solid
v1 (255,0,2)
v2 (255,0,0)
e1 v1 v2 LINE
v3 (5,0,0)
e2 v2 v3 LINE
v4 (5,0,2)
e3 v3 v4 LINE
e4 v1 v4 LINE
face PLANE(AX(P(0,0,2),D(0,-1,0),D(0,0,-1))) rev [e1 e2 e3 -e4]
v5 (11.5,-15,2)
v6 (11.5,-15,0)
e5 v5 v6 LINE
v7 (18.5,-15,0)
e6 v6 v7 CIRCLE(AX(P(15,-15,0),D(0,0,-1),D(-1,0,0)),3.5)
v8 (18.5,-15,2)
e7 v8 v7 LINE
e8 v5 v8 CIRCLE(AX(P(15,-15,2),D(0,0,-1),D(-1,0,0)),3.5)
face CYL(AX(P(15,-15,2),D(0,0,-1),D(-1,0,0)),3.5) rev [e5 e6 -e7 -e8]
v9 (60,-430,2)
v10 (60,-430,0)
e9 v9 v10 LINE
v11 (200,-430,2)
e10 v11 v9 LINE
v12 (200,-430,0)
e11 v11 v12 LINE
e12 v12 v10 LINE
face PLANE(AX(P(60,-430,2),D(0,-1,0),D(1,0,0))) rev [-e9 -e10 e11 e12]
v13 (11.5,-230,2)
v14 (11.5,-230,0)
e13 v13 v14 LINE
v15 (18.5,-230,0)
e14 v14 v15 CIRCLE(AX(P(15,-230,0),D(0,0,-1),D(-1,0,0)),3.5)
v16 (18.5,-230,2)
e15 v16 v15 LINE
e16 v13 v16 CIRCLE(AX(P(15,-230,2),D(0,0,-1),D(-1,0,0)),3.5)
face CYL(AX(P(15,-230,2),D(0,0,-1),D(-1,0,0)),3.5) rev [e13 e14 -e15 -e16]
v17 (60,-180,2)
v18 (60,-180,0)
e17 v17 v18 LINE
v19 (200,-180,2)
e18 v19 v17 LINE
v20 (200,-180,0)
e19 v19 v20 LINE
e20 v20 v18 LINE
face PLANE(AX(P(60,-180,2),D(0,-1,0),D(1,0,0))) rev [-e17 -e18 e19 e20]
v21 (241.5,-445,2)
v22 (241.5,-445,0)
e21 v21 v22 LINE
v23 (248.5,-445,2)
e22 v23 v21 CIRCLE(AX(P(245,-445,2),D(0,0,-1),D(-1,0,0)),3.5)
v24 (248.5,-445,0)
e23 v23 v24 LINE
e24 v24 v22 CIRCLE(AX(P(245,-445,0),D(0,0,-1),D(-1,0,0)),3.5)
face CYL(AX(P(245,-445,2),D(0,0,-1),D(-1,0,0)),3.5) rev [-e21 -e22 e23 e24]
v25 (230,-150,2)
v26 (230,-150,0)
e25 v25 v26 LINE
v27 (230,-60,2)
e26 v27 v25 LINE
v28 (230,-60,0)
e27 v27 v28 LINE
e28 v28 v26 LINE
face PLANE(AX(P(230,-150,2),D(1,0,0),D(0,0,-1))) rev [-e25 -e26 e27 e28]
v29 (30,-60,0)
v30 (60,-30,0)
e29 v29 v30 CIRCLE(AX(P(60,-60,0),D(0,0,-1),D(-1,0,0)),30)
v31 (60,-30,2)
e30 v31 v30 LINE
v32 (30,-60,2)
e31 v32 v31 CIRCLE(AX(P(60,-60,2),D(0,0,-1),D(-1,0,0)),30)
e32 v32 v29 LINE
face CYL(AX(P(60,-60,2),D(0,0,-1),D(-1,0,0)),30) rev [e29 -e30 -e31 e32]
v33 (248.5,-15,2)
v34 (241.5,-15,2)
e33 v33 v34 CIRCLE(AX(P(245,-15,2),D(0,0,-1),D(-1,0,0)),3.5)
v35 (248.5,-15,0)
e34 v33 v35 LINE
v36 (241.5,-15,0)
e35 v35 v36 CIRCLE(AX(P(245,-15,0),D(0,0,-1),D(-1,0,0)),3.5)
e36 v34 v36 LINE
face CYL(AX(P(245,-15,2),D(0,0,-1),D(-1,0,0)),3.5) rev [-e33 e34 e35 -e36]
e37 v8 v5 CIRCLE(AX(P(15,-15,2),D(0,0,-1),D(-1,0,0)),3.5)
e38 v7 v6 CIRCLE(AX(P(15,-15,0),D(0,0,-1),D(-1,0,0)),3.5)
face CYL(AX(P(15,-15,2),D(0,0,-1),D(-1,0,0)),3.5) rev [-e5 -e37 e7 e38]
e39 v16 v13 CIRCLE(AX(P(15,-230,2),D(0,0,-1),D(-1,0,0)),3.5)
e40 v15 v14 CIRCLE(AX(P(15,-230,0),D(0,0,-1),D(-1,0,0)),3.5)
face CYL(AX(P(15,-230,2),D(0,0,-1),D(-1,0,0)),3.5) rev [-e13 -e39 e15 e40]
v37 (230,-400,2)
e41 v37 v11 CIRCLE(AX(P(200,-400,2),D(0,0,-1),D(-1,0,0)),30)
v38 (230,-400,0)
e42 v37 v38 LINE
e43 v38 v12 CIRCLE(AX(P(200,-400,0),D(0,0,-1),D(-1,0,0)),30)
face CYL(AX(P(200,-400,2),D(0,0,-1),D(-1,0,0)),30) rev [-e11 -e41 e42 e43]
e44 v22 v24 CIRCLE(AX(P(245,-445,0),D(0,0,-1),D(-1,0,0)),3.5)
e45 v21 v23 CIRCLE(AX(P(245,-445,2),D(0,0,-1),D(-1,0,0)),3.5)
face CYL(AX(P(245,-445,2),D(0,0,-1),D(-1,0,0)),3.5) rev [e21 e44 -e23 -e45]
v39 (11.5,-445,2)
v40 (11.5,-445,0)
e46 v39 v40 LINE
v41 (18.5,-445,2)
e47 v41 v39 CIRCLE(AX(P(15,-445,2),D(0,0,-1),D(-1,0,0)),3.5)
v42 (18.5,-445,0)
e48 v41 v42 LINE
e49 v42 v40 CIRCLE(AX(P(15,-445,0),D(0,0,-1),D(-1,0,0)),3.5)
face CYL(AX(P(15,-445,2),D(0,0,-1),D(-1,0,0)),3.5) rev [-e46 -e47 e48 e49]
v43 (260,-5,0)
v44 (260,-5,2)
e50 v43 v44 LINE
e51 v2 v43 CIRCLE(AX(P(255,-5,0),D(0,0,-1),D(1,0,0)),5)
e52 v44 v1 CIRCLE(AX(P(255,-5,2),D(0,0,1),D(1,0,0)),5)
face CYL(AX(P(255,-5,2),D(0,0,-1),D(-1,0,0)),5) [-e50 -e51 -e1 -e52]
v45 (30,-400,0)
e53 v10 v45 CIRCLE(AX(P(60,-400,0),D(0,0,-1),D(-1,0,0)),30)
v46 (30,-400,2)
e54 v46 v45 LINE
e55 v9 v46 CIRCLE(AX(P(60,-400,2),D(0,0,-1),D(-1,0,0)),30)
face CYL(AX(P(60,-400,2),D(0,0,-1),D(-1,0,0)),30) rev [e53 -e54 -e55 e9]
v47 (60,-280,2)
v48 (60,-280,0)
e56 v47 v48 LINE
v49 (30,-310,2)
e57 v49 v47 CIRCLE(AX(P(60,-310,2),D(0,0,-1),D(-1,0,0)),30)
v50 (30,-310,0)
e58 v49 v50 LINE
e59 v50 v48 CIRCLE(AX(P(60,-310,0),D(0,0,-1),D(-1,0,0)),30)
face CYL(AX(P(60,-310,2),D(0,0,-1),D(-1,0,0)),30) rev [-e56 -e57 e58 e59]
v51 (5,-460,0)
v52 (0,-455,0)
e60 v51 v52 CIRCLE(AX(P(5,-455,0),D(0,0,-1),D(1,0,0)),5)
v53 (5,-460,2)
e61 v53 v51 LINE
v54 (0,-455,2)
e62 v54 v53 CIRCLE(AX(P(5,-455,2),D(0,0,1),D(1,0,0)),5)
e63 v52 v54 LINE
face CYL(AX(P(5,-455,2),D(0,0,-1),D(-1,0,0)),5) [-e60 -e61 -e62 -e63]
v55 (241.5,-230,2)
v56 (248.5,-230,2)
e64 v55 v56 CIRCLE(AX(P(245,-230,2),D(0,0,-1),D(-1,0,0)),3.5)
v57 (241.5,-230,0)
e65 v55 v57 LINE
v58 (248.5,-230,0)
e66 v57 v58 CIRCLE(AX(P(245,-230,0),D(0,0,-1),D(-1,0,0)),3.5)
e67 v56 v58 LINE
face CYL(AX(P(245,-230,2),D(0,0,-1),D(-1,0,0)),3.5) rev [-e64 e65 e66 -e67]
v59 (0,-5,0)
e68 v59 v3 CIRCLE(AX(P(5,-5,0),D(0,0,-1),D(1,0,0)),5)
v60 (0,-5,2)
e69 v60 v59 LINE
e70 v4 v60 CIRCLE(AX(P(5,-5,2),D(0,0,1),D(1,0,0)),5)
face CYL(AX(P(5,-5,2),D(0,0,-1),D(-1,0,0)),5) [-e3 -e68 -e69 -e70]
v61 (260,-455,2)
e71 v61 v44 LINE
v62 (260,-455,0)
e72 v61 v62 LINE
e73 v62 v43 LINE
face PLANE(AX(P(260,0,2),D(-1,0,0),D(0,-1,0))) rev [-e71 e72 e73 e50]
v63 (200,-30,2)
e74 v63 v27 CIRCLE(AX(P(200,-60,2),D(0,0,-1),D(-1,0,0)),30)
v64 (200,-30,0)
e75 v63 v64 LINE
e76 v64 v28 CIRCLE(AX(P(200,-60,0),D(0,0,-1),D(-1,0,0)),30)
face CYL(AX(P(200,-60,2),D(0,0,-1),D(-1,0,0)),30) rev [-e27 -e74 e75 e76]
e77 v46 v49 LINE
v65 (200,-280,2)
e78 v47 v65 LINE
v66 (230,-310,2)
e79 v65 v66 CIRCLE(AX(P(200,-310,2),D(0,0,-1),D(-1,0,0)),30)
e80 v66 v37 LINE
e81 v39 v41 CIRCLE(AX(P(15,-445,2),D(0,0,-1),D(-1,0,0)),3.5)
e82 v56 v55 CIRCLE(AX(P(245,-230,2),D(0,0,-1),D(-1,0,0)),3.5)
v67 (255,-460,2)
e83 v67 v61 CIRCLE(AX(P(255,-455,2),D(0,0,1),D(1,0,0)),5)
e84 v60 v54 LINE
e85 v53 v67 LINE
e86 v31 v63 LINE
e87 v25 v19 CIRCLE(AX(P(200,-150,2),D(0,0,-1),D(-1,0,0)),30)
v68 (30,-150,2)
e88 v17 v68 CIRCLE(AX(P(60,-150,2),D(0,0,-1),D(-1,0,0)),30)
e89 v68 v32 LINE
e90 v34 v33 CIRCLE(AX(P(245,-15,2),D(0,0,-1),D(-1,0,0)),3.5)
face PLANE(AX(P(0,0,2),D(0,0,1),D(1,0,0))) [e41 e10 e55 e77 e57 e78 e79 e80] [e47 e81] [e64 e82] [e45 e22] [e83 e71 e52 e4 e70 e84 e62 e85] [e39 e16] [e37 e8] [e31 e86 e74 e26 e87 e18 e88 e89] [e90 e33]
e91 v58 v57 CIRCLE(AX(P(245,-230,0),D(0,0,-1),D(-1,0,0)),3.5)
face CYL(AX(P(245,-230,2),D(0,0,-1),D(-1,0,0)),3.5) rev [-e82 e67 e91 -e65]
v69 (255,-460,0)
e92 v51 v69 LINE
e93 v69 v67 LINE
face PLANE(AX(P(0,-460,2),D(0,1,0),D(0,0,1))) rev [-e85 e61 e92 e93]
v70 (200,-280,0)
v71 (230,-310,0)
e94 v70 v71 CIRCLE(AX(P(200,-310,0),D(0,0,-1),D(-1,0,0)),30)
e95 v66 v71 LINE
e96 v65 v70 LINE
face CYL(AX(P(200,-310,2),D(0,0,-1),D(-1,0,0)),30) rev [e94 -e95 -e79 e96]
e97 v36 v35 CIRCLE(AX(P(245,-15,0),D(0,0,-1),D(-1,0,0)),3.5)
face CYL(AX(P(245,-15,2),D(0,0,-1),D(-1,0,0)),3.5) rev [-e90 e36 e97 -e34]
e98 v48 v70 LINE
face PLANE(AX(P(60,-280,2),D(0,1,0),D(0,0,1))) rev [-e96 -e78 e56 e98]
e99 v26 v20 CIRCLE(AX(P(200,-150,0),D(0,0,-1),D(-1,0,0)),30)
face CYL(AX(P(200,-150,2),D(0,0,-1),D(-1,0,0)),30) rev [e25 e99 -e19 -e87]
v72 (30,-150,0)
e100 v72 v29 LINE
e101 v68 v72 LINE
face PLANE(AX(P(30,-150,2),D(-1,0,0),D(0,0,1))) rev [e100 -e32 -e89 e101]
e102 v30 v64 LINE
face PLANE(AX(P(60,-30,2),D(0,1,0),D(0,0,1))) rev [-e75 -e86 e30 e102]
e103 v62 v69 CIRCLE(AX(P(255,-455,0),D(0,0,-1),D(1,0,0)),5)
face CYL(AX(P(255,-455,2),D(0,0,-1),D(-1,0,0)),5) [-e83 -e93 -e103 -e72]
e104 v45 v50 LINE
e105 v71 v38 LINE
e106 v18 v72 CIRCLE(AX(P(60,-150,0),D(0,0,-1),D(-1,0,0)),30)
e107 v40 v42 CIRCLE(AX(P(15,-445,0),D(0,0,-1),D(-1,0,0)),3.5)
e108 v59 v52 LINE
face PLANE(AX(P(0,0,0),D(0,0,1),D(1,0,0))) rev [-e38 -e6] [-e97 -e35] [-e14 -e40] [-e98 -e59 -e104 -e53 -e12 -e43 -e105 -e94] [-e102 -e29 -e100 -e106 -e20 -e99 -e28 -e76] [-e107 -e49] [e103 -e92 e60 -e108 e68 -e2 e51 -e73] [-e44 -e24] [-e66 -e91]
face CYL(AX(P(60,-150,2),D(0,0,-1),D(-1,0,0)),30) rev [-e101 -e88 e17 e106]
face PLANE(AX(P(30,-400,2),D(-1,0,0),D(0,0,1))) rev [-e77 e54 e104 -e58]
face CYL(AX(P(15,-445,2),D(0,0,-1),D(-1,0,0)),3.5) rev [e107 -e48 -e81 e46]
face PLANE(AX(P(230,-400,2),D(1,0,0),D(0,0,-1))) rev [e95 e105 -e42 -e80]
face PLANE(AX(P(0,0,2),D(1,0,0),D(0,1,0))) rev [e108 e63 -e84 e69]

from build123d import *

# Parameters (mm, degrees)
SKETCH_1_W          = 260
SKETCH_1_H          = 460
EXTRUDE_1_DEPTH     = 2
FILLET_1_R          = 5
SKETCH_2_R          = 3.5
CUT_EXTRUDE_1_DEPTH = 529.397577587
CUT_EXTRUDE_2_DEPTH = 529.397577587


with BuildPart() as part:
    # 草图1 → 凸台-拉伸1 (new body)
    with BuildSketch(Plane.XY):
        with Locations((130, -230)):
            Rectangle(SKETCH_1_W, SKETCH_1_H)
    extrude(amount=EXTRUDE_1_DEPTH)

    # 圆角1
    fillet_1_edges = [part.edges().sort_by_distance(p)[0] for p in [
        (0, 0, 1),
        (260, 0, 1),
        (260, -460, 1),
        (0, -460, 1),
    ]]
    fillet(fillet_1_edges, radius=FILLET_1_R)

    # 草图2 → 切除-拉伸1 (cut, through all)
    with BuildSketch(Plane(origin=(0, 0, 0), x_dir=(-1, 0, 0), z_dir=(0, 0, -1))):
        with Locations((-245, -445)):
            Circle(SKETCH_2_R)
        with Locations((-15, -445)):
            Circle(SKETCH_2_R)
        with Locations((-245, -15)):
            Circle(SKETCH_2_R)
        with Locations((-15, -15)):
            Circle(SKETCH_2_R)
        with Locations((-245, -230)):
            Circle(SKETCH_2_R)
        with Locations((-15, -230)):
            Circle(SKETCH_2_R)
    extrude(amount=-CUT_EXTRUDE_1_DEPTH, mode=Mode.SUBTRACT)

    # 草图3 → 切除-拉伸2 (cut, through all)
    with BuildSketch(Plane(origin=(0, 0, 0), x_dir=(-1, 0, 0), z_dir=(0, 0, -1))):
        with BuildLine():
            Line((-60, -430), (-200, -430))
            ThreePointArc((-200, -430), (-221.213203436, -421.213203436), (-230, -400))
            Line((-230, -400), (-230, -310))
            ThreePointArc((-230, -310), (-221.213203436, -288.786796564), (-200, -280))
            Line((-200, -280), (-60, -280))
            ThreePointArc((-60, -280), (-38.786796564, -288.786796564), (-30, -310))
            Line((-30, -310), (-30, -400))
            ThreePointArc((-30, -400), (-38.786796564, -421.213203436), (-60, -430))
        make_face()
        with BuildLine():
            Line((-60, -180), (-200, -180))
            ThreePointArc((-200, -180), (-221.213203436, -171.213203436), (-230, -150))
            Line((-230, -150), (-230, -60))
            ThreePointArc((-230, -60), (-221.213203436, -38.786796564), (-200, -30))
            Line((-200, -30), (-60, -30))
            ThreePointArc((-60, -30), (-38.786796564, -38.786796564), (-30, -60))
            Line((-30, -60), (-30, -150))
            ThreePointArc((-30, -150), (-38.786796564, -171.213203436), (-60, -180))
        make_face()
    extrude(amount=-CUT_EXTRUDE_2_DEPTH, mode=Mode.SUBTRACT)


solid = part.part
